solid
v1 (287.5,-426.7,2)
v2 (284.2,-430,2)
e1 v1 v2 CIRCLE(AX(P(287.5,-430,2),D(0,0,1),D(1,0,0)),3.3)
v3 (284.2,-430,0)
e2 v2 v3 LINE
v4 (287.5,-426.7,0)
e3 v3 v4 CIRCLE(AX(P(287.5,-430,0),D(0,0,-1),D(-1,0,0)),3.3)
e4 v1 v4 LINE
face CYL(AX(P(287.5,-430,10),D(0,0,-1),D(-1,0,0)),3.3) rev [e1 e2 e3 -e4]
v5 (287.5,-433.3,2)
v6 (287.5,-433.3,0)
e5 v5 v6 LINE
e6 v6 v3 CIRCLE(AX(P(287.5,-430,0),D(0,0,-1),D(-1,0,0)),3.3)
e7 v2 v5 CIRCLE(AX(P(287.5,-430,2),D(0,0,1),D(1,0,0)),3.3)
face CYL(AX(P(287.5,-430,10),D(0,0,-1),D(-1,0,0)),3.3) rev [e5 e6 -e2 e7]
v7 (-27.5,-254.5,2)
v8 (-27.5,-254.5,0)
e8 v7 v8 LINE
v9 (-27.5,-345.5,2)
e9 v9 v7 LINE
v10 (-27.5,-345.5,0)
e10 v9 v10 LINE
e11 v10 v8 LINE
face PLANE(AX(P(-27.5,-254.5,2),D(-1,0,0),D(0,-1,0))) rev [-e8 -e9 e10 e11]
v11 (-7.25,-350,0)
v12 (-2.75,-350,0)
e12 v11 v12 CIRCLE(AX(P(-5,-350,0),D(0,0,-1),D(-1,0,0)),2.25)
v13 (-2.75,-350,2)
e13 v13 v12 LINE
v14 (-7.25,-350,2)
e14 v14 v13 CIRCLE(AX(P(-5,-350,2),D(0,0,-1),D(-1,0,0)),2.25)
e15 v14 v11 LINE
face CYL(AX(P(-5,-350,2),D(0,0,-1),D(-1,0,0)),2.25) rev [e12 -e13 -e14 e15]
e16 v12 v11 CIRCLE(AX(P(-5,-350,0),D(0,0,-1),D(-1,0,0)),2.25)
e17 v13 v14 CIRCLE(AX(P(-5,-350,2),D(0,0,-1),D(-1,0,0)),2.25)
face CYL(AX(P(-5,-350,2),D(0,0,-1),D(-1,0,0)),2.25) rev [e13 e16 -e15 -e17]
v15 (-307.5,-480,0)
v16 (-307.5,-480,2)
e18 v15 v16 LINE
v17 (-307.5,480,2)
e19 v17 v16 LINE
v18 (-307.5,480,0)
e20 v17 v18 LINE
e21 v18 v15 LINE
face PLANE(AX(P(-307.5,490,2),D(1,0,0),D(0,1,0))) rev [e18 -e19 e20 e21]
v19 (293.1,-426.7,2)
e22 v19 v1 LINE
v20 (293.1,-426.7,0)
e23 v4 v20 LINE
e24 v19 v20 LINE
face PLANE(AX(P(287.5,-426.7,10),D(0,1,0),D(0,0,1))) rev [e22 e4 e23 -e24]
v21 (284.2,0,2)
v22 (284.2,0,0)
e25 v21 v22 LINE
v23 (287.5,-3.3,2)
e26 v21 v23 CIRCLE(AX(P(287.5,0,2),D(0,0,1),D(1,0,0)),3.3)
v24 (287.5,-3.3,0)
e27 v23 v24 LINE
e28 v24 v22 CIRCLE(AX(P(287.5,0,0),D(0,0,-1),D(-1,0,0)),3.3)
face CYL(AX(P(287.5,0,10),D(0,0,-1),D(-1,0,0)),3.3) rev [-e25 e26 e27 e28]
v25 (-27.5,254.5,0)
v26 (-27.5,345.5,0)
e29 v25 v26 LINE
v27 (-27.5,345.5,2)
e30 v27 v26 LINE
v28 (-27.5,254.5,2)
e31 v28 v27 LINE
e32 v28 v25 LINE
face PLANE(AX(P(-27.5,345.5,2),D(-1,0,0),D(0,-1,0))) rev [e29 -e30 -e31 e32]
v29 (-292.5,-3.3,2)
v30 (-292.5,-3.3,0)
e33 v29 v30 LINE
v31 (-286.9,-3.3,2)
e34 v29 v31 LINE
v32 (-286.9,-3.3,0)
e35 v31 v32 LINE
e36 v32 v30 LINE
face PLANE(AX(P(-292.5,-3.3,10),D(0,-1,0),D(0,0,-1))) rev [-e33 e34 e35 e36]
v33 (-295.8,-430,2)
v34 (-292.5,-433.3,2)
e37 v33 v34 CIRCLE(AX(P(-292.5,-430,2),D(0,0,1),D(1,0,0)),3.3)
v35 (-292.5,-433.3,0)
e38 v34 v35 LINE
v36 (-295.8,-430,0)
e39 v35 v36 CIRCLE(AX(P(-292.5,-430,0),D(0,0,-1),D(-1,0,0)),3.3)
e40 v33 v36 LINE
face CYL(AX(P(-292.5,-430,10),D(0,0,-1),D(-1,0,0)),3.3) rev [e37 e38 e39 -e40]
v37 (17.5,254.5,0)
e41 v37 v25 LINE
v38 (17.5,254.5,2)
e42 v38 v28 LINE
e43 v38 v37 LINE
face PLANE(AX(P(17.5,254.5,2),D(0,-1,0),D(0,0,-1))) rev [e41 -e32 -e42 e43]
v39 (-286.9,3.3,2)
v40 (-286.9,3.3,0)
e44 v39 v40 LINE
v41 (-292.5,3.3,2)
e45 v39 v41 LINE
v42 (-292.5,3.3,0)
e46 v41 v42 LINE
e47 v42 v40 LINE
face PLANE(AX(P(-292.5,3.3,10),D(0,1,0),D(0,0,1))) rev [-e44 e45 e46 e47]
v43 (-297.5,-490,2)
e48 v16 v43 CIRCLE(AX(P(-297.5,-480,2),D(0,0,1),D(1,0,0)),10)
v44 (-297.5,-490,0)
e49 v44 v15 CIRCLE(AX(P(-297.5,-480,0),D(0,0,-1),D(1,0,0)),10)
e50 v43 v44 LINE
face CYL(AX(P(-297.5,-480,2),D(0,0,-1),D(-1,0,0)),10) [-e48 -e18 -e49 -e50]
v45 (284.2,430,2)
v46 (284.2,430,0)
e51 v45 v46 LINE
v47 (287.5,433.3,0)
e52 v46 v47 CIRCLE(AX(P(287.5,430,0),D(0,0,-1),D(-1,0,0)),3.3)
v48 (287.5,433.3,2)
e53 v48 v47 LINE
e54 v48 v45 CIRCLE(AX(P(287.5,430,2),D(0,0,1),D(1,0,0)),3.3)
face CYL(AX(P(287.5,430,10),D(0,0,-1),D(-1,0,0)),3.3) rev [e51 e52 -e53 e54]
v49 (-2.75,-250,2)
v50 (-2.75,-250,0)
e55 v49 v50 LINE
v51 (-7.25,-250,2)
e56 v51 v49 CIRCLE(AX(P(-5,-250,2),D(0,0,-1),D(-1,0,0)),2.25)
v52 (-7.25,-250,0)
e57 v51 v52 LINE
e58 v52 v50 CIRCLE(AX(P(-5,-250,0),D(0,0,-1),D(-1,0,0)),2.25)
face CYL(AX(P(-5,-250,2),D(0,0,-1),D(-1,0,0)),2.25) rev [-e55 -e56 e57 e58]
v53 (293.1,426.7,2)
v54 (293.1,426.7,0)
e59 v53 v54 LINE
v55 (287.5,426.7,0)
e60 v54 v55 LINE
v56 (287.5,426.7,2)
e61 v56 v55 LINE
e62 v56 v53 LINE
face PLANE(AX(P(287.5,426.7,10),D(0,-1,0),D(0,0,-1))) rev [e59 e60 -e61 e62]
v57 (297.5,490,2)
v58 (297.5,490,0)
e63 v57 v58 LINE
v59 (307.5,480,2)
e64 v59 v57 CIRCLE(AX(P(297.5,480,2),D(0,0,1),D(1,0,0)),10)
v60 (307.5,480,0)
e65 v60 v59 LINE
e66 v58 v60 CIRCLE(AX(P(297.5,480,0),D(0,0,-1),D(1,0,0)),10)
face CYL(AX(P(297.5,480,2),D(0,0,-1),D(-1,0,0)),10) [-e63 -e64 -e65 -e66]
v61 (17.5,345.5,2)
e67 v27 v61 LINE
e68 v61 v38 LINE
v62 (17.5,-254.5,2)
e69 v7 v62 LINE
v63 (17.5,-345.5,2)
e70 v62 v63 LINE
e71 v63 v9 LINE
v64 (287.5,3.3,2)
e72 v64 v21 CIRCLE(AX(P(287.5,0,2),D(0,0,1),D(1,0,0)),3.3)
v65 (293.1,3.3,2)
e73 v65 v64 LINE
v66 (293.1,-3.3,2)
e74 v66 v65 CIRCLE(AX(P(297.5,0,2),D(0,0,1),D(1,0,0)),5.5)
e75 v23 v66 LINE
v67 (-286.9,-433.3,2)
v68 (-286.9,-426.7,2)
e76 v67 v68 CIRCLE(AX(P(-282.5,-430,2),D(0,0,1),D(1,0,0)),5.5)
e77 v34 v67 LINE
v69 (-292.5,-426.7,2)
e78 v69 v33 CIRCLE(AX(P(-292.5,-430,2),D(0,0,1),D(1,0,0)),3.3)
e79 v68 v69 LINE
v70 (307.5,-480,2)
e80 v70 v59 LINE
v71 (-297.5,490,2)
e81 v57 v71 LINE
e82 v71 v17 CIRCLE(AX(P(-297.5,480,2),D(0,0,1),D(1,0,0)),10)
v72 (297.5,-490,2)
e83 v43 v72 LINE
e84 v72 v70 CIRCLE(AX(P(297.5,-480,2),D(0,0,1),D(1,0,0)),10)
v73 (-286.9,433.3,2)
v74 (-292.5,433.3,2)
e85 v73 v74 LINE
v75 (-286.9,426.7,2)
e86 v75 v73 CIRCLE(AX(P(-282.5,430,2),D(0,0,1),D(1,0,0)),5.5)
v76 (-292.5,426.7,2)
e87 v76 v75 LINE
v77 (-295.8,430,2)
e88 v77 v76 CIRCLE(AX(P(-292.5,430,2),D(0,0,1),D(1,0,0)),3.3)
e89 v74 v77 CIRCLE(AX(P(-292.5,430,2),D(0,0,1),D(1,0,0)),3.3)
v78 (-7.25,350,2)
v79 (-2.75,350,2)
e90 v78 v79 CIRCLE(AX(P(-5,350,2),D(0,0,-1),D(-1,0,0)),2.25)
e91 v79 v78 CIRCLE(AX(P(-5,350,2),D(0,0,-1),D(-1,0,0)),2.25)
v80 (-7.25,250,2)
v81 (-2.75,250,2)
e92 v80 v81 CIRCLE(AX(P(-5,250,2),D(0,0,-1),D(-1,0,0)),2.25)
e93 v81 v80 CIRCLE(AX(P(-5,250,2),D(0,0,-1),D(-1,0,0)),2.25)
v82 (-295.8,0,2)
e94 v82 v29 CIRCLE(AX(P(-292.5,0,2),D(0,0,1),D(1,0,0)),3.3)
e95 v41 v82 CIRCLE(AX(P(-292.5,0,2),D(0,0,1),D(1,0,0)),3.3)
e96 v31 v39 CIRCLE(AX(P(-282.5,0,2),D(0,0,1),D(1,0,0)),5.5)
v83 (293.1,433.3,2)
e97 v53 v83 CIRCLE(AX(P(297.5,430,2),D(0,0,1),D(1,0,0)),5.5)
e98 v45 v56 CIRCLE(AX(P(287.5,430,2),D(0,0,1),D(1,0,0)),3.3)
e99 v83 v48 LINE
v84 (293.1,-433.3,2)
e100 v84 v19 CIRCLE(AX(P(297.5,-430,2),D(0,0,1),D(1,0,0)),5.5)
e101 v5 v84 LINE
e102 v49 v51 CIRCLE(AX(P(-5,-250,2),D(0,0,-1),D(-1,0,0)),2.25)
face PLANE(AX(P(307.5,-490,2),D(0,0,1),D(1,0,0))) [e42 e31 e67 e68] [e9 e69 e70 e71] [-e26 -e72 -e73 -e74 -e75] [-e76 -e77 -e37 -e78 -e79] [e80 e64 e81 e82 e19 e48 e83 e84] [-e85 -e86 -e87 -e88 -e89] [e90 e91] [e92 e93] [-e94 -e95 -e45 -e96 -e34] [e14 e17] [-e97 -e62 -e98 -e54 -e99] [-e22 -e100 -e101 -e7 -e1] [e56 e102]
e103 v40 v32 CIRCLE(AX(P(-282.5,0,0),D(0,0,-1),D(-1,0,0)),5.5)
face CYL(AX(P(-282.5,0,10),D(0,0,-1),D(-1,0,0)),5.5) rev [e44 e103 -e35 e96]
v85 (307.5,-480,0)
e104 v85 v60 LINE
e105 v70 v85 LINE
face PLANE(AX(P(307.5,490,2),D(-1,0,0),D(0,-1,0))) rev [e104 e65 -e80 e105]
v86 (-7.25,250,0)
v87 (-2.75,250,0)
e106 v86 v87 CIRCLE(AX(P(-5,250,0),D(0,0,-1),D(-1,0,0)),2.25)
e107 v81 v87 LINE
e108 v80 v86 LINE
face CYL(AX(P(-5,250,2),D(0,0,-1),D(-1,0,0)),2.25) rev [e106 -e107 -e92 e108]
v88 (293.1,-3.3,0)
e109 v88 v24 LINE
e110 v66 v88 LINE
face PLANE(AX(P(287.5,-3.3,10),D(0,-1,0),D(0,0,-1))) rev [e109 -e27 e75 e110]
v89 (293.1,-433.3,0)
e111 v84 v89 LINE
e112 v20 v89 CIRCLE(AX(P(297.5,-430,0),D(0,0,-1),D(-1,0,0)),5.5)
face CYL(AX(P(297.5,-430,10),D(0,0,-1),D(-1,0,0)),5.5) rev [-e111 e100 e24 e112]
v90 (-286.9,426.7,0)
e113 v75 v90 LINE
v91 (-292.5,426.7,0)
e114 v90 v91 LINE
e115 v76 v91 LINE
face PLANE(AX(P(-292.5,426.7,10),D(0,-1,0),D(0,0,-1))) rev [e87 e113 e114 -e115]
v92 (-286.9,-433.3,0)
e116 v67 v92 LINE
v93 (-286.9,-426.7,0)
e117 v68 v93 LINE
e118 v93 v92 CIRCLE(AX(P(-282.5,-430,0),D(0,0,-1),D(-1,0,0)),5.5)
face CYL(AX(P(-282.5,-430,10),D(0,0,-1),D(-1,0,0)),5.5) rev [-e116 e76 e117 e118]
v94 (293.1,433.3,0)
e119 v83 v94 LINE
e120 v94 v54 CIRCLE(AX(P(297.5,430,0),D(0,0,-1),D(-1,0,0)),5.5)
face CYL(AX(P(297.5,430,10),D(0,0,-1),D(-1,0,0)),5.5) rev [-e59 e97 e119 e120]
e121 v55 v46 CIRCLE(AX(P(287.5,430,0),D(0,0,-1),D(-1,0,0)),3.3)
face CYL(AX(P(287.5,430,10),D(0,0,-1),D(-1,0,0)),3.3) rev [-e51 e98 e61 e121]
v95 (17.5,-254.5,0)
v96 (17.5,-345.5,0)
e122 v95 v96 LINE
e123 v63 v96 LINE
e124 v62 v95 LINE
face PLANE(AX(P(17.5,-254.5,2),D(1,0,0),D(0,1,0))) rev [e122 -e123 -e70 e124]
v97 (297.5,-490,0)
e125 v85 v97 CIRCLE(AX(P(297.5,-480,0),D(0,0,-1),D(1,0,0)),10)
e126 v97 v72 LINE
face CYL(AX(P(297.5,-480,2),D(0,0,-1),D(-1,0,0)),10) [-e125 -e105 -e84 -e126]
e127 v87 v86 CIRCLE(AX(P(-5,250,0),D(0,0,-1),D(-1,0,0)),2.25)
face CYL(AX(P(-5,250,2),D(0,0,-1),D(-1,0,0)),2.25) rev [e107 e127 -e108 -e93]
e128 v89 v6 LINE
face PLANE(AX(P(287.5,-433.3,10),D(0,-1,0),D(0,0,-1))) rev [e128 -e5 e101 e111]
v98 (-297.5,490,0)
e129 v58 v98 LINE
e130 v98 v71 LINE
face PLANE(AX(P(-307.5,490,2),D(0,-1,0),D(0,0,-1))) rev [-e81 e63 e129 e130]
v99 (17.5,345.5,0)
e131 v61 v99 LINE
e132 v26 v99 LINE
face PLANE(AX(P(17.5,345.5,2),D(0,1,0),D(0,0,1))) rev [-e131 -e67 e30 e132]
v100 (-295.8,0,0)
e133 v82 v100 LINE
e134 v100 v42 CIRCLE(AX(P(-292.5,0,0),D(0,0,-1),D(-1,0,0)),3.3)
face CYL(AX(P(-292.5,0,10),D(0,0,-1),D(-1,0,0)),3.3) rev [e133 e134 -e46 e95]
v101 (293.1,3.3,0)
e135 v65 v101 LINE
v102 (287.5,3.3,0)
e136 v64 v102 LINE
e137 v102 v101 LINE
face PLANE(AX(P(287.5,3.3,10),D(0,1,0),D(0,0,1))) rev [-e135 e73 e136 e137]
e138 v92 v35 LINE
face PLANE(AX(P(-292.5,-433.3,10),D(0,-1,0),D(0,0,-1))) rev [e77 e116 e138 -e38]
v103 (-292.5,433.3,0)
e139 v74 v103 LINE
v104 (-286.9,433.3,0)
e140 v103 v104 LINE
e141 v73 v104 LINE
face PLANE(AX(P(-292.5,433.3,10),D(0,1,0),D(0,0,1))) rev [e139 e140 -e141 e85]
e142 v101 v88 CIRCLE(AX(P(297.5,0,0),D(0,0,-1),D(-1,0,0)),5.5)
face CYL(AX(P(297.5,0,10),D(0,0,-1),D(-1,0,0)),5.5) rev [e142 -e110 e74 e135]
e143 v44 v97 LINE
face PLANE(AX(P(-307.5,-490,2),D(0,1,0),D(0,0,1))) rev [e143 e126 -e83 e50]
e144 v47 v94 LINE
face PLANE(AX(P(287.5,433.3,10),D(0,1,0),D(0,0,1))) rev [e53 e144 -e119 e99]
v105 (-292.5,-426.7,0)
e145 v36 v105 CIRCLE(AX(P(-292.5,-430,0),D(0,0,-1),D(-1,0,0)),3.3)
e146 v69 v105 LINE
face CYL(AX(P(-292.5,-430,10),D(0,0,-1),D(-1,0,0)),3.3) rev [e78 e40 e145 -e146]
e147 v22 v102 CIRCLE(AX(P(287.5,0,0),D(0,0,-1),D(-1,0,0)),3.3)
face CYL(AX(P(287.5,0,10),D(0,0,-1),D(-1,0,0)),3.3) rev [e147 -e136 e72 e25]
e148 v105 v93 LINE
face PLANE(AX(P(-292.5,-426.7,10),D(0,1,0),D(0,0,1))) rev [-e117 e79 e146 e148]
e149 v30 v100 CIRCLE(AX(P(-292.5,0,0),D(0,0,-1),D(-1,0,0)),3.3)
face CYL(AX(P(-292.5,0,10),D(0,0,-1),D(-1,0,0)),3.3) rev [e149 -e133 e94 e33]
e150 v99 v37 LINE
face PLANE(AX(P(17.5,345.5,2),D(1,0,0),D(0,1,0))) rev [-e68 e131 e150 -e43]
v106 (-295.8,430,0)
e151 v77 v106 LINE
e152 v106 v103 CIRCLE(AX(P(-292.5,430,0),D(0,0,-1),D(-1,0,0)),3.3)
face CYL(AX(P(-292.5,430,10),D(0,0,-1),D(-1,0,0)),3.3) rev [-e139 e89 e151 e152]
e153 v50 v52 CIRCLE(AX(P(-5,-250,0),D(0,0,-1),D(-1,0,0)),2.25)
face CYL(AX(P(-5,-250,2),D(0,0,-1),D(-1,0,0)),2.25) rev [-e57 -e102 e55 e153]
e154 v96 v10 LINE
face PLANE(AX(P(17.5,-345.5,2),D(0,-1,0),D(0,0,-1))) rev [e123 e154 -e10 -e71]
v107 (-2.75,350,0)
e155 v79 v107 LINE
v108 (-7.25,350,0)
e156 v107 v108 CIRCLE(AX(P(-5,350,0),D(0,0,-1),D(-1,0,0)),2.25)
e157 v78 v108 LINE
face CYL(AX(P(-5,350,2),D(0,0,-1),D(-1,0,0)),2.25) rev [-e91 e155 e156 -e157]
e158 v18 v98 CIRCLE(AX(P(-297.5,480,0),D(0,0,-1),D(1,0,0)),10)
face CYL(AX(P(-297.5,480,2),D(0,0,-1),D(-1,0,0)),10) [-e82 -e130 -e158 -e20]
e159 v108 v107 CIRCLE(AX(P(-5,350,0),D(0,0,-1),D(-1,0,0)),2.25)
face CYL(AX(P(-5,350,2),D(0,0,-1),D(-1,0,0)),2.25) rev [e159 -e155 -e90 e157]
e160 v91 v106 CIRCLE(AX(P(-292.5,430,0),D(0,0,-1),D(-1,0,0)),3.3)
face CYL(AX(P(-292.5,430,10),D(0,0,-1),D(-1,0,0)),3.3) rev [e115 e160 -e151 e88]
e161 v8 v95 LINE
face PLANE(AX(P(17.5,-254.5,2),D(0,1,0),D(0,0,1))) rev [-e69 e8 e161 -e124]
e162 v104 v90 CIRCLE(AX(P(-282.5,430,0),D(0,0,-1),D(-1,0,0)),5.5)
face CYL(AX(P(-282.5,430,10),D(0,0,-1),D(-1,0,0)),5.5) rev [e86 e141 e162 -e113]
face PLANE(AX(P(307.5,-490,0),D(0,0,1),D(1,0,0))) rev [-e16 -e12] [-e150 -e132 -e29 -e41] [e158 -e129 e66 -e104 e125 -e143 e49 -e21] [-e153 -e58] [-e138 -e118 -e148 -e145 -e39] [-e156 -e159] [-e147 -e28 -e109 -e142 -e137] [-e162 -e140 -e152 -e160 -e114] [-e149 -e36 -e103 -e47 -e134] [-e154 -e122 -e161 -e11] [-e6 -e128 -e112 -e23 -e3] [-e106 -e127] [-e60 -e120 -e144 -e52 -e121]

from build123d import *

# Parameters (mm, degrees)
SKETCH1_W            = 615
SKETCH1_H            = 980
BOSS_EXTRUDE1_DEPTH  = 2
SKETCH7_W            = 45
SKETCH7_H            = 91
CUT_EXTRUDE4_DEPTH   = 579.498271389
SKETCH8_R            = 2.25
CUT_EXTRUDE5_DEPTH   = 579.498271389
FILLET3_R            = 10
CUT_EXTRUDE6_DEPTH   = 10
LPATTERN1_COUNT      = 3
LPATTERN1_PITCH      = 430
LPATTERN1_COUNT_DIR2 = 2
LPATTERN1_PITCH_DIR2 = 580


with BuildPart() as part:
    # Sketch1 → Boss-Extrude1 (new body)
    with BuildSketch(Plane.XY):
        Rectangle(SKETCH1_W, SKETCH1_H)
    extrude(amount=BOSS_EXTRUDE1_DEPTH)

    # Sketch7 → Cut-Extrude4 (cut, through all)
    with BuildSketch(Plane(origin=(0, 0, 0), x_dir=(-1, 0, 0), z_dir=(0, 0, -1))):
        with Locations((5, 300)):
            Rectangle(SKETCH7_W, SKETCH7_H)
        with Locations((5, -300)):
            Rectangle(SKETCH7_W, SKETCH7_H)
    extrude(amount=-CUT_EXTRUDE4_DEPTH, mode=Mode.SUBTRACT)

    # Sketch8 → Cut-Extrude5 (cut, through all)
    with BuildSketch(Plane(origin=(0, 0, 0), x_dir=(-1, 0, 0), z_dir=(0, 0, -1))):
        with Locations((5, 350)):
            Circle(SKETCH8_R)
        with Locations((5, 250)):
            Circle(SKETCH8_R)
        with Locations((5, -250)):
            Circle(SKETCH8_R)
        with Locations((5, -350)):
            Circle(SKETCH8_R)
    extrude(amount=-CUT_EXTRUDE5_DEPTH, mode=Mode.SUBTRACT)

    # Fillet3
    fillet3_edges = [part.edges().sort_by_distance(p)[0] for p in [
        (307.5, -490, 1),
        (-307.5, -490, 1),
        (-307.5, 490, 1),
        (307.5, 490, 1),
    ]]
    fillet(fillet3_edges, radius=FILLET3_R)

    # Sketch10 → Cut-Extrude6 (cut)
    with BuildSketch(Plane(origin=(0, 0, 0), x_dir=(-1, 0, 0), z_dir=(0, 0, -1))):
        with BuildLine():
            Line((292.5, 433.3), (286.9, 433.3))
            ThreePointArc((286.9, 433.3), (277, 430), (286.9, 426.7))
            Line((286.9, 426.7), (292.5, 426.7))
            ThreePointArc((292.5, 426.7), (295.8, 430), (292.5, 433.3))
        make_face()
    cut_extrude6 = extrude(amount=-CUT_EXTRUDE6_DEPTH, mode=Mode.SUBTRACT)

    # LPattern1: Cut-Extrude6 3 × 2
    with Locations(*[(j * LPATTERN1_PITCH_DIR2, -i * LPATTERN1_PITCH, 0) for i in range(LPATTERN1_COUNT) for j in range(LPATTERN1_COUNT_DIR2) if (i, j) != (0, 0)]):
        add(cut_extrude6, mode=Mode.SUBTRACT)


solid = part.part
